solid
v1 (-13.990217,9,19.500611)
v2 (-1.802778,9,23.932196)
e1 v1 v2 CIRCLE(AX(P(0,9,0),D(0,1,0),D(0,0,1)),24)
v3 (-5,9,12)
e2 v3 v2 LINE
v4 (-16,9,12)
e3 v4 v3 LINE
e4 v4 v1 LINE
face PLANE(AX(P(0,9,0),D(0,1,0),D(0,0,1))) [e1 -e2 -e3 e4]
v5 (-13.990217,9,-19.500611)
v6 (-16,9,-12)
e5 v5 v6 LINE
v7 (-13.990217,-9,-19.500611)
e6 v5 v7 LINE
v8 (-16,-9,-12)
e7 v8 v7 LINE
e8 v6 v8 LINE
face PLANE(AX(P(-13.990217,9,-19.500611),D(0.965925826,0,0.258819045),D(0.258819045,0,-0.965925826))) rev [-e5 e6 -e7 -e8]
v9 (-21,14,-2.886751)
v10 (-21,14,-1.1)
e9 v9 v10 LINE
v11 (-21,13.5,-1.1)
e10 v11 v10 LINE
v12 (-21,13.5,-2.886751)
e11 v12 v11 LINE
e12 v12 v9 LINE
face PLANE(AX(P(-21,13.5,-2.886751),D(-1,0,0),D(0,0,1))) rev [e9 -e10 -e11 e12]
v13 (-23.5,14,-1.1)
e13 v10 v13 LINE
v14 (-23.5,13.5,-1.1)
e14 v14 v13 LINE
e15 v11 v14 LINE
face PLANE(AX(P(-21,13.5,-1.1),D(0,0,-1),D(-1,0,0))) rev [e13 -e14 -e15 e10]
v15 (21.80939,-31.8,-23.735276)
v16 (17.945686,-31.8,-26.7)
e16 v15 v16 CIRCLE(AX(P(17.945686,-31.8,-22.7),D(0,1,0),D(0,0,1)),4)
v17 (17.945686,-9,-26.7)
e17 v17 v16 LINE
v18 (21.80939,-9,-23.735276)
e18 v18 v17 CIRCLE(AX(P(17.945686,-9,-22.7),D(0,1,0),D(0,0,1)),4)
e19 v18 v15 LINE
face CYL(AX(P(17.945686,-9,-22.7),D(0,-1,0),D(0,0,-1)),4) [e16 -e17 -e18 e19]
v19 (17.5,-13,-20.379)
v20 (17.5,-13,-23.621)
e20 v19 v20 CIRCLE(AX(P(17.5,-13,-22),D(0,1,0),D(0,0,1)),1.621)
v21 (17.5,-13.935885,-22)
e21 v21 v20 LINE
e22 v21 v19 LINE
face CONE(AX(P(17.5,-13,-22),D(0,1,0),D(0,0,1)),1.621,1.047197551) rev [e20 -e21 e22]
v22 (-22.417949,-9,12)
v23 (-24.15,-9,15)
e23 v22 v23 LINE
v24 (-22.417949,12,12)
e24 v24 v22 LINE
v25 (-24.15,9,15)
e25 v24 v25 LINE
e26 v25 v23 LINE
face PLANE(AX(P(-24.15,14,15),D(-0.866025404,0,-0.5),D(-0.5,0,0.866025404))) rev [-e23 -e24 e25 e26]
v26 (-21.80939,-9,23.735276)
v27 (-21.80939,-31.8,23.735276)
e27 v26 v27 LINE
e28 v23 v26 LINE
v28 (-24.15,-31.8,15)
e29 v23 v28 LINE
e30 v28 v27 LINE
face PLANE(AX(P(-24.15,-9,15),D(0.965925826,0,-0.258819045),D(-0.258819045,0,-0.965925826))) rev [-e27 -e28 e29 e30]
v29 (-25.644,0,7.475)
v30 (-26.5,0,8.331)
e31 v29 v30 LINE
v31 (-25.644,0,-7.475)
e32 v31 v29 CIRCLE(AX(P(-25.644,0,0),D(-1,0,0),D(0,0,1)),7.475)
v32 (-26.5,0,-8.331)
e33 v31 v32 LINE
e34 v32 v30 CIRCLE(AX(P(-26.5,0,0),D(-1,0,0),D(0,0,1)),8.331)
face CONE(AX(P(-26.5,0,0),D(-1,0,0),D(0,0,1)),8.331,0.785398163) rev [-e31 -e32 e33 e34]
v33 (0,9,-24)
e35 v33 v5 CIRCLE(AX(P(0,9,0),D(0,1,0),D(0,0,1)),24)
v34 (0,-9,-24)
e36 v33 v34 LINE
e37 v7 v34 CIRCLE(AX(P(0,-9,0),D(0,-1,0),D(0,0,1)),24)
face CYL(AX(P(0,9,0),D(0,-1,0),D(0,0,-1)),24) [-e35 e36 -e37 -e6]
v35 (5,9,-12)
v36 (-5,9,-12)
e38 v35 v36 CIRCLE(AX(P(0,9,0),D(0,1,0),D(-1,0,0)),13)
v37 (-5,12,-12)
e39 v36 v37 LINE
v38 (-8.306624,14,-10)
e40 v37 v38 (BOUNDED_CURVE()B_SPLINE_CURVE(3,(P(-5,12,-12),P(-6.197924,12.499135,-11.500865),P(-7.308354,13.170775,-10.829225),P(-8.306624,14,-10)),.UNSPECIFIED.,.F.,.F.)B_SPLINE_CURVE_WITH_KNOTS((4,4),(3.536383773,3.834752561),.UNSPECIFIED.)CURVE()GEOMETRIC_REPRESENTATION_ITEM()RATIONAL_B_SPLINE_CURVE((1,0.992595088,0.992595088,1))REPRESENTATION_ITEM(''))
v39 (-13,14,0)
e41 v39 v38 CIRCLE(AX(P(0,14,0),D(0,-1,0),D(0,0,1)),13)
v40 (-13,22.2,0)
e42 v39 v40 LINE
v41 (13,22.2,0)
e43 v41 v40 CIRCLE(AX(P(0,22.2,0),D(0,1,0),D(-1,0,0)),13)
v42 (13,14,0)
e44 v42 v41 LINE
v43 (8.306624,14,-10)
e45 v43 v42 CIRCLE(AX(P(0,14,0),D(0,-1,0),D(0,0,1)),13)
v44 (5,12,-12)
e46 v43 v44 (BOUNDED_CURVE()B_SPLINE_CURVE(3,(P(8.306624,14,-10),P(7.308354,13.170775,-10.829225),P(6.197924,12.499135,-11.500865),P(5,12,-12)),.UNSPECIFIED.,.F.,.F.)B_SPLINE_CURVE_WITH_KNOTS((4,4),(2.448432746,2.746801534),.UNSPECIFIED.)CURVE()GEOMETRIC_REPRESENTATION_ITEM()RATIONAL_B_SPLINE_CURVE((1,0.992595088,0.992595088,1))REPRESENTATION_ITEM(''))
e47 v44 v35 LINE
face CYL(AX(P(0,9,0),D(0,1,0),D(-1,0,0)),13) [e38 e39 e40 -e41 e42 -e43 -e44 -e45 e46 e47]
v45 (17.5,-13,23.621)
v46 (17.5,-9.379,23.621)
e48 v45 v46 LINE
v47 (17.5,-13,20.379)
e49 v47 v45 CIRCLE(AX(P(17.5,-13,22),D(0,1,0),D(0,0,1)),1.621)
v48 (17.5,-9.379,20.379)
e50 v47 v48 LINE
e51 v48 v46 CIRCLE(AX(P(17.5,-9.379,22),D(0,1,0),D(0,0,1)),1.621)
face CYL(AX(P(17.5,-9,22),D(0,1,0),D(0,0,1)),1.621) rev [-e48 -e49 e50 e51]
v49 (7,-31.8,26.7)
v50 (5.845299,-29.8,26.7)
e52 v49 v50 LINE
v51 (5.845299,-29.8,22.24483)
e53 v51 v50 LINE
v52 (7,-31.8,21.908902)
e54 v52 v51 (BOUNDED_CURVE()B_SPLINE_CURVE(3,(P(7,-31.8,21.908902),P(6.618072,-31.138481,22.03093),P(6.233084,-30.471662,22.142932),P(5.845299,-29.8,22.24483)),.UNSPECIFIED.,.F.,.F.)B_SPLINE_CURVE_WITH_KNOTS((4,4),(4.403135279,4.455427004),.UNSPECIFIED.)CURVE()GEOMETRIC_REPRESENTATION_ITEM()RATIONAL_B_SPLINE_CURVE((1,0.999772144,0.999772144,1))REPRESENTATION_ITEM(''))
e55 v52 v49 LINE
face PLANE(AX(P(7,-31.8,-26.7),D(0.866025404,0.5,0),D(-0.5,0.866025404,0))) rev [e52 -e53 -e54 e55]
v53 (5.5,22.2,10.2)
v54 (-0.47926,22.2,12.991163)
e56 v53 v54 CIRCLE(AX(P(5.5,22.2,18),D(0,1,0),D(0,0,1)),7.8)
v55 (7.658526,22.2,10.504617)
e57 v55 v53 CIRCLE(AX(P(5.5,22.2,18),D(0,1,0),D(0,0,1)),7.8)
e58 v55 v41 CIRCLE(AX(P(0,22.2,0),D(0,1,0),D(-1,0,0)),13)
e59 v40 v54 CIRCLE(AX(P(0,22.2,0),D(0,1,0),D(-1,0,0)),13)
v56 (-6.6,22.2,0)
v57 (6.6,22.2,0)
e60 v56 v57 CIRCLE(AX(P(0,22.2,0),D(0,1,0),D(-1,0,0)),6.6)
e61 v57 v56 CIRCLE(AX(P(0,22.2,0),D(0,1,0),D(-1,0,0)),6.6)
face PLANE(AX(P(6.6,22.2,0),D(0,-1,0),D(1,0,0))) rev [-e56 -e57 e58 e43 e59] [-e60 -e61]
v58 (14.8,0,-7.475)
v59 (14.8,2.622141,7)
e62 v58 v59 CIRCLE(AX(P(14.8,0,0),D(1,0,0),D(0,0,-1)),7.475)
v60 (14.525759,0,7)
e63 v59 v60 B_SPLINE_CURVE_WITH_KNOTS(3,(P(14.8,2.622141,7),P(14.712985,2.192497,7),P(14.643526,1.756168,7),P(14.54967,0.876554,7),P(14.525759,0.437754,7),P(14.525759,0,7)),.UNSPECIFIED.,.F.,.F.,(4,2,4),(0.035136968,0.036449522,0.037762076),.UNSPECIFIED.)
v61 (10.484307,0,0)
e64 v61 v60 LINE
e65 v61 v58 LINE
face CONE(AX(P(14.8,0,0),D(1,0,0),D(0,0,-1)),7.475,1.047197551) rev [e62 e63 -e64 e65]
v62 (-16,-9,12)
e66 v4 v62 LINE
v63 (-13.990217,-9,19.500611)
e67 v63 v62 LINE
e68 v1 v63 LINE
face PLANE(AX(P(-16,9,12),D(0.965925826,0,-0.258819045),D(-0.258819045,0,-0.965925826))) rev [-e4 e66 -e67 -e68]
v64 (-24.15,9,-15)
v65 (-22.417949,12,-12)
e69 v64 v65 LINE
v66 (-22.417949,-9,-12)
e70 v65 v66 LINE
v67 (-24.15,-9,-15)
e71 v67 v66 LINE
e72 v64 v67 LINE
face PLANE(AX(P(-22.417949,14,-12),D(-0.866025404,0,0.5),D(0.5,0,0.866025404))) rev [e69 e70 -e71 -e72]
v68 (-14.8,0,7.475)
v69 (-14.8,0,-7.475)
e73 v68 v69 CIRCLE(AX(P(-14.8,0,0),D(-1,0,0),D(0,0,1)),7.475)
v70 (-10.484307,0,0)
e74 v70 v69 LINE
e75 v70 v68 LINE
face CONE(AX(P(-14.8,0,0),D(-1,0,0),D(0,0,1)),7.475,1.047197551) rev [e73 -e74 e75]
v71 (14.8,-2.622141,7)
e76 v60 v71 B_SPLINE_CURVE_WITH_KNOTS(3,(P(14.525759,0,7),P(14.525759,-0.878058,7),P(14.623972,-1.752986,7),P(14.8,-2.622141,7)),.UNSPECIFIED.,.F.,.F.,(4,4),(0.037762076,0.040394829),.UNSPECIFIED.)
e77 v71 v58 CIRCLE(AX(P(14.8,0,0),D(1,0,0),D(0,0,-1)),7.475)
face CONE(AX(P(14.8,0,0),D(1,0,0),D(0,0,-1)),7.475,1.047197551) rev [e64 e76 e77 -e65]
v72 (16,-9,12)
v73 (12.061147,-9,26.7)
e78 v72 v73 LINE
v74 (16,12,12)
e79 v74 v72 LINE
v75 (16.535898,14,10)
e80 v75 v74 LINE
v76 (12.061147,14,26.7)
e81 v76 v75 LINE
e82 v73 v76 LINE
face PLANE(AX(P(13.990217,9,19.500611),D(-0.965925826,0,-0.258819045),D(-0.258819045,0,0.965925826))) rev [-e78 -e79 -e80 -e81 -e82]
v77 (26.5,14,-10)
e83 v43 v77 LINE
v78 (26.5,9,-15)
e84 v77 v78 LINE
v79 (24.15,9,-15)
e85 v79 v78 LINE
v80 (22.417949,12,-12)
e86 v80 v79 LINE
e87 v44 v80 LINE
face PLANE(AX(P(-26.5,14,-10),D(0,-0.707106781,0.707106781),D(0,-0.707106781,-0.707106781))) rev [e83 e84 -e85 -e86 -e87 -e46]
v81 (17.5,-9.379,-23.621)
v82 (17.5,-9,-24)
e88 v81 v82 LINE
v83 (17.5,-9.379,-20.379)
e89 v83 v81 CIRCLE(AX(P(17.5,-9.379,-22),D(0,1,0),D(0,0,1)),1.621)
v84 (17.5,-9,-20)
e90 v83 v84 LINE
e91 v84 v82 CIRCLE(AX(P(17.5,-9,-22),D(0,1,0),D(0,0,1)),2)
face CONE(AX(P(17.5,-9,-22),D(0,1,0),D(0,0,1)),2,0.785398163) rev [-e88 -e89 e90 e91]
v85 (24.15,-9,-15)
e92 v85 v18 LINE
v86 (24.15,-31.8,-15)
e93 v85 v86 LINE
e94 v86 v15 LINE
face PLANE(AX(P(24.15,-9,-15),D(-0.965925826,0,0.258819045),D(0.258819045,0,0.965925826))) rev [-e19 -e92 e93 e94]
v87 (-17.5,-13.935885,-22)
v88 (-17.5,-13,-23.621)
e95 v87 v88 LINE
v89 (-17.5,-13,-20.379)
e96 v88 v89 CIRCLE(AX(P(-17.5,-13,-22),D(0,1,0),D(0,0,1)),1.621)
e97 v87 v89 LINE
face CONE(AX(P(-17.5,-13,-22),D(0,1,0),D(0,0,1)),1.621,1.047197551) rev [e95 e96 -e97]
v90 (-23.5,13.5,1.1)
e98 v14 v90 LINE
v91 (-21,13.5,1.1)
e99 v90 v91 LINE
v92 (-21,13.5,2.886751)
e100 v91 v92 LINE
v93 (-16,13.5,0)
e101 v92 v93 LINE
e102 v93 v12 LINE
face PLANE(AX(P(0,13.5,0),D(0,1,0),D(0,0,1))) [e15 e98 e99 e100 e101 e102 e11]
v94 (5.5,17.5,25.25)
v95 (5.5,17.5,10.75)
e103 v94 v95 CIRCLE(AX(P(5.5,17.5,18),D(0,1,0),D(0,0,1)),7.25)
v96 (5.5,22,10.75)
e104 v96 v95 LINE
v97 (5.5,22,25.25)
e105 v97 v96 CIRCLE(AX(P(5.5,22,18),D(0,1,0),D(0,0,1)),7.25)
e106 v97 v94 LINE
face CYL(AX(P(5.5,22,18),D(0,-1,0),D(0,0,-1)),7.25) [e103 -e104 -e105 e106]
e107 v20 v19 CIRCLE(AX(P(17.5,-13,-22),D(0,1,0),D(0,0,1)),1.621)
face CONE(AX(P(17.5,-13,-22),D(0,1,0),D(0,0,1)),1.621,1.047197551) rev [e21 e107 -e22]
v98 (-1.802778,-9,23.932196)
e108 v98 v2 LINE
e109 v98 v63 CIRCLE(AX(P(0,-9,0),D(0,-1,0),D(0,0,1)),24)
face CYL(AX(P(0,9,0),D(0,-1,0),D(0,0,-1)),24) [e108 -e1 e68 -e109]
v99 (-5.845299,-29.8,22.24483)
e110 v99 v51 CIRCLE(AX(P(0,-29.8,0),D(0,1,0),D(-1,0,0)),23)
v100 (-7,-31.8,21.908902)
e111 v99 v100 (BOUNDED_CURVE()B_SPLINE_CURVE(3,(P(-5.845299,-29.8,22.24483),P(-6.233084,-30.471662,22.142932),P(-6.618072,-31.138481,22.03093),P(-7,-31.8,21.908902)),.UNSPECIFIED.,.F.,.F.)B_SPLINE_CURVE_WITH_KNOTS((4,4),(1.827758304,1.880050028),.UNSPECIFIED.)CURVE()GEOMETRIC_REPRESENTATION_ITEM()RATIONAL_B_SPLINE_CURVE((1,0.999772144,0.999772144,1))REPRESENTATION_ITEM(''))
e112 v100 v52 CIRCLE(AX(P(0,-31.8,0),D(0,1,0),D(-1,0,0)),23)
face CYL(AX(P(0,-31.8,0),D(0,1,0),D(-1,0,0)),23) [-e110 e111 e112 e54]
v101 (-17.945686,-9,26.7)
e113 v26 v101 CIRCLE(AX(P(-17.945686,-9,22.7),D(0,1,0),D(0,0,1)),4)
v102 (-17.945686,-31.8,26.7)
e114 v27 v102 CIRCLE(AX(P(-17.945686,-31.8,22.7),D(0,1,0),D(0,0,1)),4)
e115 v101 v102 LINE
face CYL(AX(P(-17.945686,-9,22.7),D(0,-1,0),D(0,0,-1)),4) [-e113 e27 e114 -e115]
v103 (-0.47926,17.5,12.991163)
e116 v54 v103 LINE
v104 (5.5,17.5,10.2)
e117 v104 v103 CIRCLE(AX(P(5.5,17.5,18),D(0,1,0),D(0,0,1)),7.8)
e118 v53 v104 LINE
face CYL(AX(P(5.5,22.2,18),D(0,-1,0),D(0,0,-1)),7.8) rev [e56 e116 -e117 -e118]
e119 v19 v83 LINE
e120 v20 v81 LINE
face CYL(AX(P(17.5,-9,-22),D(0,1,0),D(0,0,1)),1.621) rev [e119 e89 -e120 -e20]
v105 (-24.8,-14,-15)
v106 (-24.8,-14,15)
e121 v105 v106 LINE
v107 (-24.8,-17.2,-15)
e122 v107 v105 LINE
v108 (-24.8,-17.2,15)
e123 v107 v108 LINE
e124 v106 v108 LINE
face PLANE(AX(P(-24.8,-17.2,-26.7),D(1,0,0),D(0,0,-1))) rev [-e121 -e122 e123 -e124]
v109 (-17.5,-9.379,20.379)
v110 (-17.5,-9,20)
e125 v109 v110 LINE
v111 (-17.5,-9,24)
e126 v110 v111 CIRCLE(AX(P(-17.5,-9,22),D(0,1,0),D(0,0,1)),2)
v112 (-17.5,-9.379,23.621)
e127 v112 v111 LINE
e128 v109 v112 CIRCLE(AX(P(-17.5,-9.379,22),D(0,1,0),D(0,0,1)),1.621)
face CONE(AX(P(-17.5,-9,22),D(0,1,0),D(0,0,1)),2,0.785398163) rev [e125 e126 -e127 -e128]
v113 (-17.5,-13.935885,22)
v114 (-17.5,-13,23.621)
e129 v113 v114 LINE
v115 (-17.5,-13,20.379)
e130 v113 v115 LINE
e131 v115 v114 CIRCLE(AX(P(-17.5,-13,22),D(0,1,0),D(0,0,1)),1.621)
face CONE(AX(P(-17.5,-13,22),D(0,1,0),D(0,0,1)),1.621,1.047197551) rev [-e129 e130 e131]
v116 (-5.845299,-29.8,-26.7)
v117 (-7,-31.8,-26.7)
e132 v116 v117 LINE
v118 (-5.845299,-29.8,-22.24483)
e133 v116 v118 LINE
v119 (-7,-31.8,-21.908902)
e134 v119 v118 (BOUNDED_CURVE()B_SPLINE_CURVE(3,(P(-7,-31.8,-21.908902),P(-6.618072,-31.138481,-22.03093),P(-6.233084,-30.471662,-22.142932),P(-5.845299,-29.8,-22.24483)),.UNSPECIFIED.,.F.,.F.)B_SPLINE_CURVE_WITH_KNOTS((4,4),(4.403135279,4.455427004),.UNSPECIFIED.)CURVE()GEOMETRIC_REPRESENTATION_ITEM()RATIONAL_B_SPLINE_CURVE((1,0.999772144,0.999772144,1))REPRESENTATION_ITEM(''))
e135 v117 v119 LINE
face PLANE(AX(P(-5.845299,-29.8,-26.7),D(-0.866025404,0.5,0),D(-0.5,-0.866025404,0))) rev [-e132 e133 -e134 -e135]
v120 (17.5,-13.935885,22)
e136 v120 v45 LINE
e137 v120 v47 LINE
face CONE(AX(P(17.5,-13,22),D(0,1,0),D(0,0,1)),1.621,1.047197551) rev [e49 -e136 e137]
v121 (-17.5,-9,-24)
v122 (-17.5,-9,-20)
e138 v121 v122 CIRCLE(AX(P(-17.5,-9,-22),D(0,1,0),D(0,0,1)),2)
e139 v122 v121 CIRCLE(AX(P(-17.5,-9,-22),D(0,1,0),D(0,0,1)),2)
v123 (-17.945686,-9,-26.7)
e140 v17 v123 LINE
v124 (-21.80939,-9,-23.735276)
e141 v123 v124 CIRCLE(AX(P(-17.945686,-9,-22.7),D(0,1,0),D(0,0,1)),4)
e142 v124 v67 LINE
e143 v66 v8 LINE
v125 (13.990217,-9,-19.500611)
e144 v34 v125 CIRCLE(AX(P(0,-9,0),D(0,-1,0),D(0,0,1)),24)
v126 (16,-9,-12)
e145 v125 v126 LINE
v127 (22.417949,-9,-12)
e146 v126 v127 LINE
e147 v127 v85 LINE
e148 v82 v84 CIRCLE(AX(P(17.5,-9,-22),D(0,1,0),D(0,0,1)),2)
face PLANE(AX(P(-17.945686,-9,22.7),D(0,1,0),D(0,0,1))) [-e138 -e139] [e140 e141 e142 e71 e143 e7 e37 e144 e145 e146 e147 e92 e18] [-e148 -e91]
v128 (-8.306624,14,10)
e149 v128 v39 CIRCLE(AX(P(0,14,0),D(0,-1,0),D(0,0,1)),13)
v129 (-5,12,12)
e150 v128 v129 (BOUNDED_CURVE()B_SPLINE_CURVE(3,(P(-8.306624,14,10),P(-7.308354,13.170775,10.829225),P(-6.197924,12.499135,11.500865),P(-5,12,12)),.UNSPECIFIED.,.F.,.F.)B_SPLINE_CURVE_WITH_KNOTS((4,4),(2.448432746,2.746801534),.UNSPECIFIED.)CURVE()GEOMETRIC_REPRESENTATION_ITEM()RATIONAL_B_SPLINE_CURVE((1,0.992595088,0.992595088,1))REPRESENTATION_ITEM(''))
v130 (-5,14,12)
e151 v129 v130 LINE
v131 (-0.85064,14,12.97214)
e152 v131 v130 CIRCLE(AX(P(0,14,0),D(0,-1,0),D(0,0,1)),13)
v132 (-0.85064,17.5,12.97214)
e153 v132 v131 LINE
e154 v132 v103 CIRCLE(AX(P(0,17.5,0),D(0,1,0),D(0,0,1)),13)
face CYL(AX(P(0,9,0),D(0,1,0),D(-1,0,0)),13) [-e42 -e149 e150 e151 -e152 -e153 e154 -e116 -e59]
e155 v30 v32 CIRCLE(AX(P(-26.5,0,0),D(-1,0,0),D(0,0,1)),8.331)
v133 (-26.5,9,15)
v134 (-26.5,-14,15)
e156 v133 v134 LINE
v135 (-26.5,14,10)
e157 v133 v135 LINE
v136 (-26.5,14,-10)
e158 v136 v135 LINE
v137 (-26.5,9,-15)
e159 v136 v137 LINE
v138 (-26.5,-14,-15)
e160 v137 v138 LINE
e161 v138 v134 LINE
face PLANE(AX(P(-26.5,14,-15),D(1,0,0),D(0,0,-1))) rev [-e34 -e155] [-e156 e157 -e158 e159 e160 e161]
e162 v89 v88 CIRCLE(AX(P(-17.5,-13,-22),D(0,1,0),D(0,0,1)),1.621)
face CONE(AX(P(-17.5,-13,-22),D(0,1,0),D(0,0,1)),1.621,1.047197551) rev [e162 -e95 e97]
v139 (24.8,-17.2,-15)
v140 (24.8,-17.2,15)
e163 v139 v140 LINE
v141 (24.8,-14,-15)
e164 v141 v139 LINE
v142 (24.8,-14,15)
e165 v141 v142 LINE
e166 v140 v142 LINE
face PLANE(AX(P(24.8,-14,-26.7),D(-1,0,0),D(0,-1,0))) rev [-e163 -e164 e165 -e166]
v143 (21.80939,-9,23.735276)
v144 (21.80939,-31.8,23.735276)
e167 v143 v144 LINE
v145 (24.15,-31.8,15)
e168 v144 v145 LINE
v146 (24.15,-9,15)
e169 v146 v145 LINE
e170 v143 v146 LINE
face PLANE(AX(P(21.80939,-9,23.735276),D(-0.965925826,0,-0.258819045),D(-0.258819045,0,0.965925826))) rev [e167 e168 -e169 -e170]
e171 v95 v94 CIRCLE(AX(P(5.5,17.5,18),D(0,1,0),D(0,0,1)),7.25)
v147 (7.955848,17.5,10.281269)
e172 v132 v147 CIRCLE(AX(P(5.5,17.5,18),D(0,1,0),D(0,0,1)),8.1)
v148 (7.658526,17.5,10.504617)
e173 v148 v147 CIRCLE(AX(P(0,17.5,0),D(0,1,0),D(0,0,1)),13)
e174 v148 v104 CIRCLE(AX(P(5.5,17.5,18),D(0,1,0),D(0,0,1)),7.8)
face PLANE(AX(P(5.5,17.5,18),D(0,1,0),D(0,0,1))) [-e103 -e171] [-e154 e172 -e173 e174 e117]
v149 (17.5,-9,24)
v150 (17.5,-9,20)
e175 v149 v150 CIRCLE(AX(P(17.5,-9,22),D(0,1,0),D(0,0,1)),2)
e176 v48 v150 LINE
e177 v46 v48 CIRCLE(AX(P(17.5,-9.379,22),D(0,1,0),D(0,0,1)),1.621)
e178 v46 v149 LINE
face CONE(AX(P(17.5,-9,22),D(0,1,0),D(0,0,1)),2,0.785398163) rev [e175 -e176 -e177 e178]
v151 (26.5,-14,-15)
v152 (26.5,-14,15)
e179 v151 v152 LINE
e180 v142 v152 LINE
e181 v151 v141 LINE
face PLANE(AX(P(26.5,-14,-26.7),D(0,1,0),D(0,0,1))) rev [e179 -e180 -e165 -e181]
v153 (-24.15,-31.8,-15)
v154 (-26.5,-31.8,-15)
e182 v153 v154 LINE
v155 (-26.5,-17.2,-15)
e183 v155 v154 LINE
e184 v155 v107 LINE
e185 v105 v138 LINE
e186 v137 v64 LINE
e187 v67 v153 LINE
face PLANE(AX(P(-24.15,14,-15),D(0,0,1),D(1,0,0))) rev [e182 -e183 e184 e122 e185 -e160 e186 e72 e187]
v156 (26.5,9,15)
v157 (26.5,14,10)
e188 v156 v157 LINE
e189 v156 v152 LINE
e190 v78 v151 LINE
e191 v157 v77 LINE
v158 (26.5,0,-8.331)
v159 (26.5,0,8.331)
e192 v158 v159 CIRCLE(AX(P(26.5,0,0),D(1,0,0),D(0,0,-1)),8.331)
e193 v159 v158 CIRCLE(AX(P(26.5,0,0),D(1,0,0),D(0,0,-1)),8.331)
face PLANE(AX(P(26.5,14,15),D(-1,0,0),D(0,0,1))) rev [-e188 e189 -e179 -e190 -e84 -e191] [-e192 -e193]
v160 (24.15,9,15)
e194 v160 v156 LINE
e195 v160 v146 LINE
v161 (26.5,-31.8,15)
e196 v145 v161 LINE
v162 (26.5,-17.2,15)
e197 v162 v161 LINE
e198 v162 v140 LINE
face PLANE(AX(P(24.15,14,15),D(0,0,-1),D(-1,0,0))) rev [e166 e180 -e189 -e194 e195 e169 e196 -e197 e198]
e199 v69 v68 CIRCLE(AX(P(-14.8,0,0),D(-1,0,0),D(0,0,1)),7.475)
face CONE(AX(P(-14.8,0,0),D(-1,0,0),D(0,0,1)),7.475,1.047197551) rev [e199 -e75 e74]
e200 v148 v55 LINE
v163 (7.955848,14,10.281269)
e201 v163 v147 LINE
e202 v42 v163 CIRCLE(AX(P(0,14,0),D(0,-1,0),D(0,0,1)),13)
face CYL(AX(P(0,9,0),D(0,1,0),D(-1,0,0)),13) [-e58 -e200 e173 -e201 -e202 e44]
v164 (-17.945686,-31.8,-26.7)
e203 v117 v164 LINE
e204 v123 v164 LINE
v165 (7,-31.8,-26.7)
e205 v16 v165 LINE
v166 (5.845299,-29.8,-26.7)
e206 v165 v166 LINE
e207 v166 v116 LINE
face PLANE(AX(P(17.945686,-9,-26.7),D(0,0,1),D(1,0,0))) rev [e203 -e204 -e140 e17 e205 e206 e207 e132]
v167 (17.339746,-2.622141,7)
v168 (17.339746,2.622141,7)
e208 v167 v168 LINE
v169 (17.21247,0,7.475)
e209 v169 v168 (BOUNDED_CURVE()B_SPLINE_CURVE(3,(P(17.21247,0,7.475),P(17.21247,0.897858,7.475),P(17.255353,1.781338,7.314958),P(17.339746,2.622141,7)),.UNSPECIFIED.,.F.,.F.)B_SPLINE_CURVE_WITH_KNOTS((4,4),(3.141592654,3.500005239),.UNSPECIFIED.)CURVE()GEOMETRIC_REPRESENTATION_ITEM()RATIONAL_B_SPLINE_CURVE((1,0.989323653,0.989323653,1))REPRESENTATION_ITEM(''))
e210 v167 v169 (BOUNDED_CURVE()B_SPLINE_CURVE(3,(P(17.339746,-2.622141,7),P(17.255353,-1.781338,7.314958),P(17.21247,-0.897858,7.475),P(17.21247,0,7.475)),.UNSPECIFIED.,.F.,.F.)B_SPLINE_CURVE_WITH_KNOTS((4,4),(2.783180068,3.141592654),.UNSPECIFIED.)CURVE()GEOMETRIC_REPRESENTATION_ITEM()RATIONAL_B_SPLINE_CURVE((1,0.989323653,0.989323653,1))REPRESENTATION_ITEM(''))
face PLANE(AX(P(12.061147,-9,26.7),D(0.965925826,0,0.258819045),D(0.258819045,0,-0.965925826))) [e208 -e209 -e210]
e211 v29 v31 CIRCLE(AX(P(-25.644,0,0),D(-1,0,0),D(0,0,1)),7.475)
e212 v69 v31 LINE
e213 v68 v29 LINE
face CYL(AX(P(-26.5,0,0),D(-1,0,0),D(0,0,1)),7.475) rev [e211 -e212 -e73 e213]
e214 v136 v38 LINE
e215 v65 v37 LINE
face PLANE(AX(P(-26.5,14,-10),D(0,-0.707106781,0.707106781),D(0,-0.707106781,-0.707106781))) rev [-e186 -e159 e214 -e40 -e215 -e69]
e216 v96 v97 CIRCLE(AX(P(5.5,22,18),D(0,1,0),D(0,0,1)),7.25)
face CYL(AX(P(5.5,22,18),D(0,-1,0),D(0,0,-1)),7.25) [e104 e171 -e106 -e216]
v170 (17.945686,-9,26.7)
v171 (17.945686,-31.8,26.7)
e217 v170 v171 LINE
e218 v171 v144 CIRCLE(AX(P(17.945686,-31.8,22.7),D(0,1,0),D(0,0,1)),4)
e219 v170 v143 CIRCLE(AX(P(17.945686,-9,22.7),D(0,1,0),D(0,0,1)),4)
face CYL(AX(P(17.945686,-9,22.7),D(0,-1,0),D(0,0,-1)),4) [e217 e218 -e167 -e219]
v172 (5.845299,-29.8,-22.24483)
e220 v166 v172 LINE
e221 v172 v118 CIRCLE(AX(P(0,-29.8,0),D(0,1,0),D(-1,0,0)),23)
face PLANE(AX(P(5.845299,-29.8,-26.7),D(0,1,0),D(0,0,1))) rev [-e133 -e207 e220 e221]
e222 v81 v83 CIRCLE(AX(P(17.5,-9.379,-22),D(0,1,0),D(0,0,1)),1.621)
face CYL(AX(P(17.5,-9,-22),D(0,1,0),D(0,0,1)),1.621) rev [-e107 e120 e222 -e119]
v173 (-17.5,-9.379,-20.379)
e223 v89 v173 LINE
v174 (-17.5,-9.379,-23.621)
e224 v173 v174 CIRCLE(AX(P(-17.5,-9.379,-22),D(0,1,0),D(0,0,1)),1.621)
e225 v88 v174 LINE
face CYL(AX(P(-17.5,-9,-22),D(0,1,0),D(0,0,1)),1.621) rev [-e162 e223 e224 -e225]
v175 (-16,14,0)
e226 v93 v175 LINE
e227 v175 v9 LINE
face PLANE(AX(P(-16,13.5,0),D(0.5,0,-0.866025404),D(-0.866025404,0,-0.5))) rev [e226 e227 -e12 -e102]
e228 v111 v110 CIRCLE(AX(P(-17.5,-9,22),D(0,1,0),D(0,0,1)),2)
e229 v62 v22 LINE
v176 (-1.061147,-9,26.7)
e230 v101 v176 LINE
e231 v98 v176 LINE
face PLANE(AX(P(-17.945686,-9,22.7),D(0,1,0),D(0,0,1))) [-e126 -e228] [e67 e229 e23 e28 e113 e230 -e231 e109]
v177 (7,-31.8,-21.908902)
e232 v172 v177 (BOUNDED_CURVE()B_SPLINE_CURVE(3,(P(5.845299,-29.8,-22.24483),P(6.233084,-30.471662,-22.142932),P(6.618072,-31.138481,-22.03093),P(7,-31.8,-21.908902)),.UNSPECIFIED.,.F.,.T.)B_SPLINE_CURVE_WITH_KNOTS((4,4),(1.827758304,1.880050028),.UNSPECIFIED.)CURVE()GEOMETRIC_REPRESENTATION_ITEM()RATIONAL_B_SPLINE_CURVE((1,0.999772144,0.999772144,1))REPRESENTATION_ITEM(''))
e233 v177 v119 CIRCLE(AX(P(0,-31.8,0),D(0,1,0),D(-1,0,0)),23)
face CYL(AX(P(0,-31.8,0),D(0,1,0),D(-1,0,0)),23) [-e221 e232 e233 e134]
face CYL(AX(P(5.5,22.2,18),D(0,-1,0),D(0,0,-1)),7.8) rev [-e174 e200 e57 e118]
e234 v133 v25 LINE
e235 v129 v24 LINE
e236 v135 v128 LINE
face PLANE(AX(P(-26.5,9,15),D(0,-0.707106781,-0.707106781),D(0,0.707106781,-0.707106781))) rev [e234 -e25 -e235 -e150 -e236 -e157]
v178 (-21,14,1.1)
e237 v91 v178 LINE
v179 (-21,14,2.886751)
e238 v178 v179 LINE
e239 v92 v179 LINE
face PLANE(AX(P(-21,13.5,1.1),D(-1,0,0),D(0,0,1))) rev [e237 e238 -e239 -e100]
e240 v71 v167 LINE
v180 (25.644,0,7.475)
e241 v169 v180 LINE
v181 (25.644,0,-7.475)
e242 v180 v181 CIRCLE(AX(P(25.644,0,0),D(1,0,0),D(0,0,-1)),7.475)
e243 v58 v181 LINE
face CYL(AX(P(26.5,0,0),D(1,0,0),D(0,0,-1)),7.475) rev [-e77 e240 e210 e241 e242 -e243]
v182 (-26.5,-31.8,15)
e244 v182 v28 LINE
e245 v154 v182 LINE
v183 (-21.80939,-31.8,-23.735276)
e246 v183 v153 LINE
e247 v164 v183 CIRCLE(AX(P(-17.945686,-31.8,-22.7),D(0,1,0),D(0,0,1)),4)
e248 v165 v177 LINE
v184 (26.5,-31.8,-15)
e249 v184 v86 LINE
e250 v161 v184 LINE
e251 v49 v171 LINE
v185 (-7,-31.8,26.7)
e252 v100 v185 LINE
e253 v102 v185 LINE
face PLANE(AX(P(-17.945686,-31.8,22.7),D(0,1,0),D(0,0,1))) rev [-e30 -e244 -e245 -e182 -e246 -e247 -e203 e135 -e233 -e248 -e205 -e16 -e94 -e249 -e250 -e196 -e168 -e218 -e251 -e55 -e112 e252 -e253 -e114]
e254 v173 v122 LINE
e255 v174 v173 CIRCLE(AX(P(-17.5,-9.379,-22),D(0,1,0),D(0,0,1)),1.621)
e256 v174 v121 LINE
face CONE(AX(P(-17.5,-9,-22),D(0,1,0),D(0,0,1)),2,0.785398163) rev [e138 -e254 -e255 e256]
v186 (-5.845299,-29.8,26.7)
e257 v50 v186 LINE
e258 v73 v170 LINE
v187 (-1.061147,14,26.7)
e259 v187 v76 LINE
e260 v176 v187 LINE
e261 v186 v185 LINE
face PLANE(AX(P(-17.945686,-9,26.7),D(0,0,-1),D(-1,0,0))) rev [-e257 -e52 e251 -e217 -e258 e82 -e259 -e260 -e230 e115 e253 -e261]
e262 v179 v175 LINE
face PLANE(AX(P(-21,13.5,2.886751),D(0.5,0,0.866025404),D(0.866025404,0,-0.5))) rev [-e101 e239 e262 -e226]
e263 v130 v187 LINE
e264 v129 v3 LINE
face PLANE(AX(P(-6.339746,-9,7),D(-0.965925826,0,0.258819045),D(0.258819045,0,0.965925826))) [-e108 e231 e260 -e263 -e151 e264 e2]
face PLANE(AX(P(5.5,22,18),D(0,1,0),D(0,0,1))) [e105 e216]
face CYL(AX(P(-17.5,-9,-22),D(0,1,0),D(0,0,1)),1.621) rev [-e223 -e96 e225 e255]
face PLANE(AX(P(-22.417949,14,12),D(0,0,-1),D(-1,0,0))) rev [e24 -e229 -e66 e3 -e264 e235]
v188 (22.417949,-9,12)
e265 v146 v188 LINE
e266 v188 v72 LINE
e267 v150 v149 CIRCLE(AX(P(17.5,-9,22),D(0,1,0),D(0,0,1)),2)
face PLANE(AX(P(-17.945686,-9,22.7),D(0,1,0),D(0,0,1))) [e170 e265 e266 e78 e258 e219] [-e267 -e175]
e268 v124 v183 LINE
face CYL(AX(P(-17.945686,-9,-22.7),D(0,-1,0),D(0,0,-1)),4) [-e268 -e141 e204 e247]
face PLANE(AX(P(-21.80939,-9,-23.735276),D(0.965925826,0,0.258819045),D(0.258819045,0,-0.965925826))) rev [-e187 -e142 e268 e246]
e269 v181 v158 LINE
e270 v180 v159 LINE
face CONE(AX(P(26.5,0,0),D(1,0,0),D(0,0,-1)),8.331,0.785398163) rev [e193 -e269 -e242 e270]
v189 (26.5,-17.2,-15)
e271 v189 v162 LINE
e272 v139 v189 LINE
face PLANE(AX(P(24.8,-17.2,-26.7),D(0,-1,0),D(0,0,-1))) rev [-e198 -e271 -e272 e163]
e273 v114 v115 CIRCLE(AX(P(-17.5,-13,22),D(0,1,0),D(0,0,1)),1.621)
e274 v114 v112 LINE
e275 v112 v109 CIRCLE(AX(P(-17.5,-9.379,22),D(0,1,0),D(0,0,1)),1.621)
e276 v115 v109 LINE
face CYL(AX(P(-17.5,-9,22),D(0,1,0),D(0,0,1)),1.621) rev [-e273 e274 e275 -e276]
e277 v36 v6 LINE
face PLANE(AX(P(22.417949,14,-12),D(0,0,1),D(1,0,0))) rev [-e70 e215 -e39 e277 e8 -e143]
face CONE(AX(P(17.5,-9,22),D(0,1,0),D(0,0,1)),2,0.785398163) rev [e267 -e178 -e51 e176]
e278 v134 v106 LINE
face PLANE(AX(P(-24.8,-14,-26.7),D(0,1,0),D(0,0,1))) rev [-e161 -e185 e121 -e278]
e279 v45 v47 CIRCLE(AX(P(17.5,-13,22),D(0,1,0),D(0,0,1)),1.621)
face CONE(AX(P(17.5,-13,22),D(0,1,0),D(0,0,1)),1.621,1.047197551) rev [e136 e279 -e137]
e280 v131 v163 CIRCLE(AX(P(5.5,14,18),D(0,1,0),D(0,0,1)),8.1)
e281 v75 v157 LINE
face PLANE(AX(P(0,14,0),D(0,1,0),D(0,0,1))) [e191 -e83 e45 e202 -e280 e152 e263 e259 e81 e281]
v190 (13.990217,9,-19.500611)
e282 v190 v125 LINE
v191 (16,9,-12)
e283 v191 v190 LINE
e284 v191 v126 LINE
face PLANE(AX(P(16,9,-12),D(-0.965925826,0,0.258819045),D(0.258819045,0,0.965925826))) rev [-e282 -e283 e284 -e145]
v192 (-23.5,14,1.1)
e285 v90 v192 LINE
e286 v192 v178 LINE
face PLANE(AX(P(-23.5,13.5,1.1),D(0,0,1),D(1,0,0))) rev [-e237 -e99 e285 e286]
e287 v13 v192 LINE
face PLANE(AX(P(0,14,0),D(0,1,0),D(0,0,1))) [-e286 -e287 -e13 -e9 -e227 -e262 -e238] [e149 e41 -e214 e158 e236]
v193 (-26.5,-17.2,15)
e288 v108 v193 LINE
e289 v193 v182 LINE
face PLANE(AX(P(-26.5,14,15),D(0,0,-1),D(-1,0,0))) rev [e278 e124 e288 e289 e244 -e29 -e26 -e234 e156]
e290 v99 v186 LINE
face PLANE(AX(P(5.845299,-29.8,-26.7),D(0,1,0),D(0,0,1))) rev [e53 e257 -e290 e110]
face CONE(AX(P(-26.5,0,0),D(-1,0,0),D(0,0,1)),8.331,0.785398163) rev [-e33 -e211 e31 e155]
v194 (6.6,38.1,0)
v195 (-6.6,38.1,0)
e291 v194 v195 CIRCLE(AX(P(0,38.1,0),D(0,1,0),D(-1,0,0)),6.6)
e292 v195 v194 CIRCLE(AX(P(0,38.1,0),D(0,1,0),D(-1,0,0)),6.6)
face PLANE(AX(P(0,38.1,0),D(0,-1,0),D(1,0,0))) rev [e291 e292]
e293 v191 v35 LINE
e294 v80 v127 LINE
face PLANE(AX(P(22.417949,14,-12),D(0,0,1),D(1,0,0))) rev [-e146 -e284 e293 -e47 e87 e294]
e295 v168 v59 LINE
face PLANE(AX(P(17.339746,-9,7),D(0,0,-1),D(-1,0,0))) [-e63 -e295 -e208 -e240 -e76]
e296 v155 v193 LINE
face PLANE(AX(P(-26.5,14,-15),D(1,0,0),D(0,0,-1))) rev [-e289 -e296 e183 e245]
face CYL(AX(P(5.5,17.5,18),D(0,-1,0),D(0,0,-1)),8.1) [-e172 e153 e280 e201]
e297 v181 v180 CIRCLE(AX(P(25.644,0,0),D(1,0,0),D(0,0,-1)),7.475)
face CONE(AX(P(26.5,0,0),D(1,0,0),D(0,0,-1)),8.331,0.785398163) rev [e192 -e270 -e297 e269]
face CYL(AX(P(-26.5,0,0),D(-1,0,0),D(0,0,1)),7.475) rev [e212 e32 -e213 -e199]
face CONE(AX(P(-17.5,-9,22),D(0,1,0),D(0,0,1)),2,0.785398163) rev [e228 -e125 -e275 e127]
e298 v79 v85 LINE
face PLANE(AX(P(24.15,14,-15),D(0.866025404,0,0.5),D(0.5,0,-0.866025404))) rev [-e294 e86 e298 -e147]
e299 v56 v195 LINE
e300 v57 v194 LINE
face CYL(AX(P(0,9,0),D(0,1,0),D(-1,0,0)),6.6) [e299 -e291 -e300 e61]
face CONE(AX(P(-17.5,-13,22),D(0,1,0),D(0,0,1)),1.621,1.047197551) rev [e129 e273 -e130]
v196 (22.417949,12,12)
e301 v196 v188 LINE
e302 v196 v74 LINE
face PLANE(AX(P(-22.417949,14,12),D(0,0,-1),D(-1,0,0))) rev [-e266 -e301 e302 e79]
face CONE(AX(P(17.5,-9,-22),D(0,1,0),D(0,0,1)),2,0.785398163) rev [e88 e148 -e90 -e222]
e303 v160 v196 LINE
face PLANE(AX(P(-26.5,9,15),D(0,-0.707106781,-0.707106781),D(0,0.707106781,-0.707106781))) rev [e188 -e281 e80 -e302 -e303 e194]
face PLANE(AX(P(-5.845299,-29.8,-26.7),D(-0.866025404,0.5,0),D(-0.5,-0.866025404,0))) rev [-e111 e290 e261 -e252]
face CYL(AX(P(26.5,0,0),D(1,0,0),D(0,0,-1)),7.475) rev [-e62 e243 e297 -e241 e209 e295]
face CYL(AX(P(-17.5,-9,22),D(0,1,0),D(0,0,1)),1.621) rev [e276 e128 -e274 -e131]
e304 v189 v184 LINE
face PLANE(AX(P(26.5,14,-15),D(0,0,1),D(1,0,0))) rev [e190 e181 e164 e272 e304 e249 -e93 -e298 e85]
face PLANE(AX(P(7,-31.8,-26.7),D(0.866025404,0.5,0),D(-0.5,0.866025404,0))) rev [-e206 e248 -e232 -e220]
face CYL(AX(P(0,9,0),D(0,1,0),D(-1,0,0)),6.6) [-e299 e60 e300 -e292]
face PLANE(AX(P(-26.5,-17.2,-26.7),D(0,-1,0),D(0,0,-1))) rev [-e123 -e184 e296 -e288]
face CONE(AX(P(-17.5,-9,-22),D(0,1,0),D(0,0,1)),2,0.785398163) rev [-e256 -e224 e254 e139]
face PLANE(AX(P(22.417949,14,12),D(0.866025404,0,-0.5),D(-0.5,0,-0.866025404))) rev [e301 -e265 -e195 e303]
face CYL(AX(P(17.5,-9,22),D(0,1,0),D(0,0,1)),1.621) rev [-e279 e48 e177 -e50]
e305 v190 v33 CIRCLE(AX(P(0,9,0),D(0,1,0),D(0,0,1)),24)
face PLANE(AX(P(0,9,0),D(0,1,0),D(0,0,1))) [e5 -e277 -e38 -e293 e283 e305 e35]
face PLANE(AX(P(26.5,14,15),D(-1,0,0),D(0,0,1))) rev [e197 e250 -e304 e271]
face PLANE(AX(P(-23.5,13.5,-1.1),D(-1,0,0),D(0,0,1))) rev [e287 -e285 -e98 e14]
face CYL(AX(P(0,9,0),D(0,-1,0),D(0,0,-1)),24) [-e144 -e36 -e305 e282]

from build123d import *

# Parameters (mm, degrees)
EXTRUDE_1_DEPTH             = 22.8
EXTRUDE_2_DEPTH             = 45.8
CUT_EXTRUDE_1_DEPTH         = 26.5
CUT_EXTRUDE_1_DEPTH_BACK    = 26.5
EXTRUDE_3_DEPTH             = 40.8
CUT_EXTRUDE_2_DEPTH         = 26.7
CUT_EXTRUDE_2_DEPTH_BACK    = 26.7
SKETCH_5_W                  = 1.7
SKETCH_5_H                  = 3.2
CUT_EXTRUDE_3_DEPTH         = 26.7
CUT_EXTRUDE_3_DEPTH_BACK    = 26.7
SKETCH_6_W                  = 1.7
SKETCH_6_H                  = 3.2
HOLE_WIZARD_1_D             = 14.95
HOLE_WIZARD_1_DEPTH         = 11.7
HOLE_WIZARD_1_CSINK_D       = 16.662
HOLE_WIZARD_1_CSINK_ANGLE   = 90
HOLE_WIZARD_1_TIP           = 4.315693262
HOLE_WIZARD_2_D             = 14.95
HOLE_WIZARD_2_DEPTH         = 11.7
HOLE_WIZARD_2_CSINK_D       = 16.662
HOLE_WIZARD_2_CSINK_ANGLE   = 90
HOLE_WIZARD_2_TIP           = 4.315693262
PATTERN_LINEAR_1_COUNT      = 2
PATTERN_LINEAR_1_PITCH      = 44
PATTERN_LINEAR_1_COUNT_DIR2 = 2
PATTERN_LINEAR_1_PITCH_DIR2 = 35
EXTRUDE_4_DEPTH             = 23
SKETCH_16_R                 = 7.8
CUT_EXTRUDE_4_DEPTH         = 8.2
SKETCH_17_R                 = 8.1
EXTRUDE_5_DEPTH             = 3.5
SKETCH_18_R                 = 7.25
EXTRUDE_6_DEPTH             = 4.5
CUT_EXTRUDE_5_DEPTH         = 0.5
CUT_EXTRUDE_6_DEPTH         = 26.7
CUT_EXTRUDE_6_DEPTH_BACK    = 26.7
SKETCH_21_W                 = 23
SKETCH_21_H                 = 2


with BuildPart() as part:
    # 草图1 → 凸台-拉伸1 (new body)
    with BuildSketch(Plane(origin=(0, -31.8, 0), x_dir=(1, 0, 0), z_dir=(0, 1, 0))):
        with BuildLine():
            Line((-24.15, -15), (-21.809389802, -23.73527618))
            ThreePointArc((-21.809389802, -23.73527618), (-20.380732213, -25.873413361), (-17.945686497, -26.7))
            Line((-17.945686497, -26.7), (17.945686497, -26.7))
            ThreePointArc((17.945686497, -26.7), (20.380732213, -25.873413361), (21.809389802, -23.73527618))
            Line((21.809389802, -23.73527618), (24.15, -15))
            Line((24.15, -15), (24.15, 15))
            Line((24.15, 15), (21.809389802, 23.73527618))
            ThreePointArc((21.809389802, 23.73527618), (20.380732213, 25.873413361), (17.945686497, 26.7))
            Line((17.945686497, 26.7), (-17.945686497, 26.7))
            ThreePointArc((-17.945686497, 26.7), (-20.380732213, 25.873413361), (-21.809389802, 23.73527618))
            Line((-21.809389802, 23.73527618), (-24.15, 15))
            Line((-24.15, 15), (-24.15, -15))
        make_face()
    extrude(amount=EXTRUDE_1_DEPTH)

    # 草图2 → 凸台-拉伸2 (add)
    with BuildSketch(Plane(origin=(0, -31.8, 0), x_dir=(1, 0, 0), z_dir=(0, 1, 0))):
        Polygon((-26.5, -15), (-24.15, -15), (-22.417949192, -12), (22.417949192, -12), (24.15, -15), (26.5, -15), (26.5, 15), (24.15, 15), (22.417949192, 12), (-22.417949192, 12), (-24.15, 15), (-26.5, 15), align=None)
    extrude(amount=EXTRUDE_2_DEPTH)

    # 草图3 → 切除-拉伸1 (cut, two sides: drawn at the far end of the back side and taken through both)
    with BuildSketch(Plane(origin=(0, 0, 0), x_dir=(0, 0, -1), z_dir=(1, 0, 0)).offset(-CUT_EXTRUDE_1_DEPTH_BACK)):
        Polygon((-26.7, 45.8), (-26.7, 0), (-15, 0), (-15, 9), (-10, 14), (10, 14), (15, 9), (15, 0), (26.7, 0), (26.7, 45.8), align=None)
    extrude(amount=CUT_EXTRUDE_1_DEPTH + CUT_EXTRUDE_1_DEPTH_BACK, mode=Mode.SUBTRACT)

    # 草图4 → 凸台-拉伸3 (add)
    with BuildSketch(Plane(origin=(0, -31.8, 0), x_dir=(1, 0, 0), z_dir=(0, 1, 0))):
        with BuildLine():
            Line((-16, -12), (-13.99021743, -19.500610664))
            ThreePointArc((-13.99021743, -19.500610664), (0, -24), (13.99021743, -19.500610664))
            Line((13.99021743, -19.500610664), (16, -12))
            Line((16, -12), (16, 12))
            Line((16, 12), (13.99021743, 19.500610664))
            ThreePointArc((13.99021743, 19.500610664), (0, 24), (-13.99021743, 19.500610664))
            Line((-13.99021743, 19.500610664), (-16, 12))
            Line((-16, 12), (-16, -12))
        make_face()
    extrude(amount=EXTRUDE_3_DEPTH)

    # 草图5 → 切除-拉伸2 (cut, two sides: drawn at the far end of the back side and taken through both)
    with BuildSketch(Plane.XY.offset(-CUT_EXTRUDE_2_DEPTH_BACK)):
        with Locations((25.65, -15.6)):
            Rectangle(SKETCH_5_W, SKETCH_5_H)
    extrude(amount=CUT_EXTRUDE_2_DEPTH + CUT_EXTRUDE_2_DEPTH_BACK, mode=Mode.SUBTRACT)

    # 草图6 → 切除-拉伸3 (cut, two sides: drawn at the far end of the back side and taken through both)
    with BuildSketch(Plane.XY.offset(-CUT_EXTRUDE_3_DEPTH_BACK)):
        with Locations((-25.65, -15.6)):
            Rectangle(SKETCH_6_W, SKETCH_6_H)
    extrude(amount=CUT_EXTRUDE_3_DEPTH + CUT_EXTRUDE_3_DEPTH_BACK, mode=Mode.SUBTRACT)

    # 孔1
    with Locations(Plane(origin=(26.5, 0, 0), x_dir=(0, 0, -1), z_dir=(1, 0, 0))):
        with Locations((0, 0)):
            CounterSinkHole(HOLE_WIZARD_1_D / 2, HOLE_WIZARD_1_CSINK_D / 2, depth=HOLE_WIZARD_1_DEPTH, counter_sink_angle=HOLE_WIZARD_1_CSINK_ANGLE)
            with Locations((0, 0, -(HOLE_WIZARD_1_DEPTH + HOLE_WIZARD_1_TIP / 2))):  # 120° drill point
                Cone(0, HOLE_WIZARD_1_D / 2, HOLE_WIZARD_1_TIP, mode=Mode.SUBTRACT)

    # 孔2
    with Locations(Plane.ZY.offset(26.5)):
        with Locations((0, 0)):
            CounterSinkHole(HOLE_WIZARD_2_D / 2, HOLE_WIZARD_2_CSINK_D / 2, depth=HOLE_WIZARD_2_DEPTH, counter_sink_angle=HOLE_WIZARD_2_CSINK_ANGLE)
            with Locations((0, 0, -(HOLE_WIZARD_2_DEPTH + HOLE_WIZARD_2_TIP / 2))):  # 120° drill point
                Cone(0, HOLE_WIZARD_2_D / 2, HOLE_WIZARD_2_TIP, mode=Mode.SUBTRACT)

    # 草图11 → 孔3 (revolve, cut)
    with BuildSketch(Plane(origin=(17.5, -9, 22), x_dir=(0, 0, 1), z_dir=(1, 0, 0))):
        Polygon((0, 0), (0, 4.935884786), (1.621, 4), (1.621, 0.379), (2, 0), align=None)
    hole_wizard_3 = revolve(axis=Axis((17.5, 5.308894879, 22), (0, -1, 0)), mode=Mode.SUBTRACT)

    # 阵列(线性)1: Hole Wizard 3 2 × 2
    with Locations(*[(-j * PATTERN_LINEAR_1_PITCH_DIR2, 0, -i * PATTERN_LINEAR_1_PITCH) for i in range(PATTERN_LINEAR_1_COUNT) for j in range(PATTERN_LINEAR_1_COUNT_DIR2) if (i, j) != (0, 0)]):
        add(hole_wizard_3, mode=Mode.SUBTRACT)

    # 草图14 → 旋转1 (revolve)
    with BuildSketch(Plane.XY, mode=Mode.PRIVATE) as revolve_1_sk:
        Polygon((0, 38.1), (6.6, 38.1), (6.6, 22.2), (13, 22.2), (13, 9), (0, 9), align=None)
    revolve(revolve_1_sk.sketch.rotate(Axis((0, 9, 0), (0, 1, 0)), 180), axis=Axis((0, 9, 0), (0, 1, 0)))

    # 草图15 → 凸台-拉伸4 (add)
    with BuildSketch(Plane(origin=(0, 14, 0), x_dir=(1, 0, 0), z_dir=(0, 1, 0))):
        Polygon((-6.339745962, -7), (-1.061146871, -26.7), (12.061146871, -26.7), (17.339745962, -7), align=None)
    extrude(amount=-EXTRUDE_4_DEPTH)

    # 草图16 → 切除-拉伸4 (cut)
    with BuildSketch(Plane(origin=(0, 14, 0), x_dir=(1, 0, 0), z_dir=(0, 1, 0))):
        with Locations((5.5, -18)):
            Circle(SKETCH_16_R)
    extrude(amount=CUT_EXTRUDE_4_DEPTH, mode=Mode.SUBTRACT)

    # 草图17 → 凸台-拉伸5 (add)
    with BuildSketch(Plane(origin=(0, 14, 0), x_dir=(1, 0, 0), z_dir=(0, 1, 0))):
        with Locations((5.5, -18)):
            Circle(SKETCH_17_R)
    extrude(amount=EXTRUDE_5_DEPTH)

    # 草图18 → 凸台-拉伸6 (add)
    with BuildSketch(Plane(origin=(0, 17.5, 0), x_dir=(1, 0, 0), z_dir=(0, 1, 0))):
        with Locations(Location((5.5, -18, 0), (0, 0, 270))):
            Circle(SKETCH_18_R)
    extrude(amount=EXTRUDE_6_DEPTH)

    # 草图19 → 切除-拉伸5 (cut)
    with BuildSketch(Plane(origin=(0, 14, 0), x_dir=(1, 0, 0), z_dir=(0, 1, 0))):
        Polygon((-23.5, -1.1), (-21, -1.1), (-21, -2.886751346), (-16, 0), (-21, 2.886751346), (-21, 1.1), (-23.5, 1.1), align=None)
    extrude(amount=-CUT_EXTRUDE_5_DEPTH, mode=Mode.SUBTRACT)

    # 草图20 → 切除-拉伸6 (cut, two sides: drawn at the far end of the back side and taken through both)
    with BuildSketch(Plane.XY.offset(-CUT_EXTRUDE_6_DEPTH_BACK)):
        Polygon((-7, -31.8), (7, -31.8), (5.845299462, -29.8), (-5.845299462, -29.8), align=None)
    extrude(amount=CUT_EXTRUDE_6_DEPTH + CUT_EXTRUDE_6_DEPTH_BACK, mode=Mode.SUBTRACT)

    # 草图21 → 旋转2 (revolve)
    with BuildSketch(Plane.XY):
        with Locations((11.5, -30.8)):
            Rectangle(SKETCH_21_W, SKETCH_21_H)
    revolve(axis=Axis((0, -31.8, 0), (0, 1, 0)))


solid = part.part
